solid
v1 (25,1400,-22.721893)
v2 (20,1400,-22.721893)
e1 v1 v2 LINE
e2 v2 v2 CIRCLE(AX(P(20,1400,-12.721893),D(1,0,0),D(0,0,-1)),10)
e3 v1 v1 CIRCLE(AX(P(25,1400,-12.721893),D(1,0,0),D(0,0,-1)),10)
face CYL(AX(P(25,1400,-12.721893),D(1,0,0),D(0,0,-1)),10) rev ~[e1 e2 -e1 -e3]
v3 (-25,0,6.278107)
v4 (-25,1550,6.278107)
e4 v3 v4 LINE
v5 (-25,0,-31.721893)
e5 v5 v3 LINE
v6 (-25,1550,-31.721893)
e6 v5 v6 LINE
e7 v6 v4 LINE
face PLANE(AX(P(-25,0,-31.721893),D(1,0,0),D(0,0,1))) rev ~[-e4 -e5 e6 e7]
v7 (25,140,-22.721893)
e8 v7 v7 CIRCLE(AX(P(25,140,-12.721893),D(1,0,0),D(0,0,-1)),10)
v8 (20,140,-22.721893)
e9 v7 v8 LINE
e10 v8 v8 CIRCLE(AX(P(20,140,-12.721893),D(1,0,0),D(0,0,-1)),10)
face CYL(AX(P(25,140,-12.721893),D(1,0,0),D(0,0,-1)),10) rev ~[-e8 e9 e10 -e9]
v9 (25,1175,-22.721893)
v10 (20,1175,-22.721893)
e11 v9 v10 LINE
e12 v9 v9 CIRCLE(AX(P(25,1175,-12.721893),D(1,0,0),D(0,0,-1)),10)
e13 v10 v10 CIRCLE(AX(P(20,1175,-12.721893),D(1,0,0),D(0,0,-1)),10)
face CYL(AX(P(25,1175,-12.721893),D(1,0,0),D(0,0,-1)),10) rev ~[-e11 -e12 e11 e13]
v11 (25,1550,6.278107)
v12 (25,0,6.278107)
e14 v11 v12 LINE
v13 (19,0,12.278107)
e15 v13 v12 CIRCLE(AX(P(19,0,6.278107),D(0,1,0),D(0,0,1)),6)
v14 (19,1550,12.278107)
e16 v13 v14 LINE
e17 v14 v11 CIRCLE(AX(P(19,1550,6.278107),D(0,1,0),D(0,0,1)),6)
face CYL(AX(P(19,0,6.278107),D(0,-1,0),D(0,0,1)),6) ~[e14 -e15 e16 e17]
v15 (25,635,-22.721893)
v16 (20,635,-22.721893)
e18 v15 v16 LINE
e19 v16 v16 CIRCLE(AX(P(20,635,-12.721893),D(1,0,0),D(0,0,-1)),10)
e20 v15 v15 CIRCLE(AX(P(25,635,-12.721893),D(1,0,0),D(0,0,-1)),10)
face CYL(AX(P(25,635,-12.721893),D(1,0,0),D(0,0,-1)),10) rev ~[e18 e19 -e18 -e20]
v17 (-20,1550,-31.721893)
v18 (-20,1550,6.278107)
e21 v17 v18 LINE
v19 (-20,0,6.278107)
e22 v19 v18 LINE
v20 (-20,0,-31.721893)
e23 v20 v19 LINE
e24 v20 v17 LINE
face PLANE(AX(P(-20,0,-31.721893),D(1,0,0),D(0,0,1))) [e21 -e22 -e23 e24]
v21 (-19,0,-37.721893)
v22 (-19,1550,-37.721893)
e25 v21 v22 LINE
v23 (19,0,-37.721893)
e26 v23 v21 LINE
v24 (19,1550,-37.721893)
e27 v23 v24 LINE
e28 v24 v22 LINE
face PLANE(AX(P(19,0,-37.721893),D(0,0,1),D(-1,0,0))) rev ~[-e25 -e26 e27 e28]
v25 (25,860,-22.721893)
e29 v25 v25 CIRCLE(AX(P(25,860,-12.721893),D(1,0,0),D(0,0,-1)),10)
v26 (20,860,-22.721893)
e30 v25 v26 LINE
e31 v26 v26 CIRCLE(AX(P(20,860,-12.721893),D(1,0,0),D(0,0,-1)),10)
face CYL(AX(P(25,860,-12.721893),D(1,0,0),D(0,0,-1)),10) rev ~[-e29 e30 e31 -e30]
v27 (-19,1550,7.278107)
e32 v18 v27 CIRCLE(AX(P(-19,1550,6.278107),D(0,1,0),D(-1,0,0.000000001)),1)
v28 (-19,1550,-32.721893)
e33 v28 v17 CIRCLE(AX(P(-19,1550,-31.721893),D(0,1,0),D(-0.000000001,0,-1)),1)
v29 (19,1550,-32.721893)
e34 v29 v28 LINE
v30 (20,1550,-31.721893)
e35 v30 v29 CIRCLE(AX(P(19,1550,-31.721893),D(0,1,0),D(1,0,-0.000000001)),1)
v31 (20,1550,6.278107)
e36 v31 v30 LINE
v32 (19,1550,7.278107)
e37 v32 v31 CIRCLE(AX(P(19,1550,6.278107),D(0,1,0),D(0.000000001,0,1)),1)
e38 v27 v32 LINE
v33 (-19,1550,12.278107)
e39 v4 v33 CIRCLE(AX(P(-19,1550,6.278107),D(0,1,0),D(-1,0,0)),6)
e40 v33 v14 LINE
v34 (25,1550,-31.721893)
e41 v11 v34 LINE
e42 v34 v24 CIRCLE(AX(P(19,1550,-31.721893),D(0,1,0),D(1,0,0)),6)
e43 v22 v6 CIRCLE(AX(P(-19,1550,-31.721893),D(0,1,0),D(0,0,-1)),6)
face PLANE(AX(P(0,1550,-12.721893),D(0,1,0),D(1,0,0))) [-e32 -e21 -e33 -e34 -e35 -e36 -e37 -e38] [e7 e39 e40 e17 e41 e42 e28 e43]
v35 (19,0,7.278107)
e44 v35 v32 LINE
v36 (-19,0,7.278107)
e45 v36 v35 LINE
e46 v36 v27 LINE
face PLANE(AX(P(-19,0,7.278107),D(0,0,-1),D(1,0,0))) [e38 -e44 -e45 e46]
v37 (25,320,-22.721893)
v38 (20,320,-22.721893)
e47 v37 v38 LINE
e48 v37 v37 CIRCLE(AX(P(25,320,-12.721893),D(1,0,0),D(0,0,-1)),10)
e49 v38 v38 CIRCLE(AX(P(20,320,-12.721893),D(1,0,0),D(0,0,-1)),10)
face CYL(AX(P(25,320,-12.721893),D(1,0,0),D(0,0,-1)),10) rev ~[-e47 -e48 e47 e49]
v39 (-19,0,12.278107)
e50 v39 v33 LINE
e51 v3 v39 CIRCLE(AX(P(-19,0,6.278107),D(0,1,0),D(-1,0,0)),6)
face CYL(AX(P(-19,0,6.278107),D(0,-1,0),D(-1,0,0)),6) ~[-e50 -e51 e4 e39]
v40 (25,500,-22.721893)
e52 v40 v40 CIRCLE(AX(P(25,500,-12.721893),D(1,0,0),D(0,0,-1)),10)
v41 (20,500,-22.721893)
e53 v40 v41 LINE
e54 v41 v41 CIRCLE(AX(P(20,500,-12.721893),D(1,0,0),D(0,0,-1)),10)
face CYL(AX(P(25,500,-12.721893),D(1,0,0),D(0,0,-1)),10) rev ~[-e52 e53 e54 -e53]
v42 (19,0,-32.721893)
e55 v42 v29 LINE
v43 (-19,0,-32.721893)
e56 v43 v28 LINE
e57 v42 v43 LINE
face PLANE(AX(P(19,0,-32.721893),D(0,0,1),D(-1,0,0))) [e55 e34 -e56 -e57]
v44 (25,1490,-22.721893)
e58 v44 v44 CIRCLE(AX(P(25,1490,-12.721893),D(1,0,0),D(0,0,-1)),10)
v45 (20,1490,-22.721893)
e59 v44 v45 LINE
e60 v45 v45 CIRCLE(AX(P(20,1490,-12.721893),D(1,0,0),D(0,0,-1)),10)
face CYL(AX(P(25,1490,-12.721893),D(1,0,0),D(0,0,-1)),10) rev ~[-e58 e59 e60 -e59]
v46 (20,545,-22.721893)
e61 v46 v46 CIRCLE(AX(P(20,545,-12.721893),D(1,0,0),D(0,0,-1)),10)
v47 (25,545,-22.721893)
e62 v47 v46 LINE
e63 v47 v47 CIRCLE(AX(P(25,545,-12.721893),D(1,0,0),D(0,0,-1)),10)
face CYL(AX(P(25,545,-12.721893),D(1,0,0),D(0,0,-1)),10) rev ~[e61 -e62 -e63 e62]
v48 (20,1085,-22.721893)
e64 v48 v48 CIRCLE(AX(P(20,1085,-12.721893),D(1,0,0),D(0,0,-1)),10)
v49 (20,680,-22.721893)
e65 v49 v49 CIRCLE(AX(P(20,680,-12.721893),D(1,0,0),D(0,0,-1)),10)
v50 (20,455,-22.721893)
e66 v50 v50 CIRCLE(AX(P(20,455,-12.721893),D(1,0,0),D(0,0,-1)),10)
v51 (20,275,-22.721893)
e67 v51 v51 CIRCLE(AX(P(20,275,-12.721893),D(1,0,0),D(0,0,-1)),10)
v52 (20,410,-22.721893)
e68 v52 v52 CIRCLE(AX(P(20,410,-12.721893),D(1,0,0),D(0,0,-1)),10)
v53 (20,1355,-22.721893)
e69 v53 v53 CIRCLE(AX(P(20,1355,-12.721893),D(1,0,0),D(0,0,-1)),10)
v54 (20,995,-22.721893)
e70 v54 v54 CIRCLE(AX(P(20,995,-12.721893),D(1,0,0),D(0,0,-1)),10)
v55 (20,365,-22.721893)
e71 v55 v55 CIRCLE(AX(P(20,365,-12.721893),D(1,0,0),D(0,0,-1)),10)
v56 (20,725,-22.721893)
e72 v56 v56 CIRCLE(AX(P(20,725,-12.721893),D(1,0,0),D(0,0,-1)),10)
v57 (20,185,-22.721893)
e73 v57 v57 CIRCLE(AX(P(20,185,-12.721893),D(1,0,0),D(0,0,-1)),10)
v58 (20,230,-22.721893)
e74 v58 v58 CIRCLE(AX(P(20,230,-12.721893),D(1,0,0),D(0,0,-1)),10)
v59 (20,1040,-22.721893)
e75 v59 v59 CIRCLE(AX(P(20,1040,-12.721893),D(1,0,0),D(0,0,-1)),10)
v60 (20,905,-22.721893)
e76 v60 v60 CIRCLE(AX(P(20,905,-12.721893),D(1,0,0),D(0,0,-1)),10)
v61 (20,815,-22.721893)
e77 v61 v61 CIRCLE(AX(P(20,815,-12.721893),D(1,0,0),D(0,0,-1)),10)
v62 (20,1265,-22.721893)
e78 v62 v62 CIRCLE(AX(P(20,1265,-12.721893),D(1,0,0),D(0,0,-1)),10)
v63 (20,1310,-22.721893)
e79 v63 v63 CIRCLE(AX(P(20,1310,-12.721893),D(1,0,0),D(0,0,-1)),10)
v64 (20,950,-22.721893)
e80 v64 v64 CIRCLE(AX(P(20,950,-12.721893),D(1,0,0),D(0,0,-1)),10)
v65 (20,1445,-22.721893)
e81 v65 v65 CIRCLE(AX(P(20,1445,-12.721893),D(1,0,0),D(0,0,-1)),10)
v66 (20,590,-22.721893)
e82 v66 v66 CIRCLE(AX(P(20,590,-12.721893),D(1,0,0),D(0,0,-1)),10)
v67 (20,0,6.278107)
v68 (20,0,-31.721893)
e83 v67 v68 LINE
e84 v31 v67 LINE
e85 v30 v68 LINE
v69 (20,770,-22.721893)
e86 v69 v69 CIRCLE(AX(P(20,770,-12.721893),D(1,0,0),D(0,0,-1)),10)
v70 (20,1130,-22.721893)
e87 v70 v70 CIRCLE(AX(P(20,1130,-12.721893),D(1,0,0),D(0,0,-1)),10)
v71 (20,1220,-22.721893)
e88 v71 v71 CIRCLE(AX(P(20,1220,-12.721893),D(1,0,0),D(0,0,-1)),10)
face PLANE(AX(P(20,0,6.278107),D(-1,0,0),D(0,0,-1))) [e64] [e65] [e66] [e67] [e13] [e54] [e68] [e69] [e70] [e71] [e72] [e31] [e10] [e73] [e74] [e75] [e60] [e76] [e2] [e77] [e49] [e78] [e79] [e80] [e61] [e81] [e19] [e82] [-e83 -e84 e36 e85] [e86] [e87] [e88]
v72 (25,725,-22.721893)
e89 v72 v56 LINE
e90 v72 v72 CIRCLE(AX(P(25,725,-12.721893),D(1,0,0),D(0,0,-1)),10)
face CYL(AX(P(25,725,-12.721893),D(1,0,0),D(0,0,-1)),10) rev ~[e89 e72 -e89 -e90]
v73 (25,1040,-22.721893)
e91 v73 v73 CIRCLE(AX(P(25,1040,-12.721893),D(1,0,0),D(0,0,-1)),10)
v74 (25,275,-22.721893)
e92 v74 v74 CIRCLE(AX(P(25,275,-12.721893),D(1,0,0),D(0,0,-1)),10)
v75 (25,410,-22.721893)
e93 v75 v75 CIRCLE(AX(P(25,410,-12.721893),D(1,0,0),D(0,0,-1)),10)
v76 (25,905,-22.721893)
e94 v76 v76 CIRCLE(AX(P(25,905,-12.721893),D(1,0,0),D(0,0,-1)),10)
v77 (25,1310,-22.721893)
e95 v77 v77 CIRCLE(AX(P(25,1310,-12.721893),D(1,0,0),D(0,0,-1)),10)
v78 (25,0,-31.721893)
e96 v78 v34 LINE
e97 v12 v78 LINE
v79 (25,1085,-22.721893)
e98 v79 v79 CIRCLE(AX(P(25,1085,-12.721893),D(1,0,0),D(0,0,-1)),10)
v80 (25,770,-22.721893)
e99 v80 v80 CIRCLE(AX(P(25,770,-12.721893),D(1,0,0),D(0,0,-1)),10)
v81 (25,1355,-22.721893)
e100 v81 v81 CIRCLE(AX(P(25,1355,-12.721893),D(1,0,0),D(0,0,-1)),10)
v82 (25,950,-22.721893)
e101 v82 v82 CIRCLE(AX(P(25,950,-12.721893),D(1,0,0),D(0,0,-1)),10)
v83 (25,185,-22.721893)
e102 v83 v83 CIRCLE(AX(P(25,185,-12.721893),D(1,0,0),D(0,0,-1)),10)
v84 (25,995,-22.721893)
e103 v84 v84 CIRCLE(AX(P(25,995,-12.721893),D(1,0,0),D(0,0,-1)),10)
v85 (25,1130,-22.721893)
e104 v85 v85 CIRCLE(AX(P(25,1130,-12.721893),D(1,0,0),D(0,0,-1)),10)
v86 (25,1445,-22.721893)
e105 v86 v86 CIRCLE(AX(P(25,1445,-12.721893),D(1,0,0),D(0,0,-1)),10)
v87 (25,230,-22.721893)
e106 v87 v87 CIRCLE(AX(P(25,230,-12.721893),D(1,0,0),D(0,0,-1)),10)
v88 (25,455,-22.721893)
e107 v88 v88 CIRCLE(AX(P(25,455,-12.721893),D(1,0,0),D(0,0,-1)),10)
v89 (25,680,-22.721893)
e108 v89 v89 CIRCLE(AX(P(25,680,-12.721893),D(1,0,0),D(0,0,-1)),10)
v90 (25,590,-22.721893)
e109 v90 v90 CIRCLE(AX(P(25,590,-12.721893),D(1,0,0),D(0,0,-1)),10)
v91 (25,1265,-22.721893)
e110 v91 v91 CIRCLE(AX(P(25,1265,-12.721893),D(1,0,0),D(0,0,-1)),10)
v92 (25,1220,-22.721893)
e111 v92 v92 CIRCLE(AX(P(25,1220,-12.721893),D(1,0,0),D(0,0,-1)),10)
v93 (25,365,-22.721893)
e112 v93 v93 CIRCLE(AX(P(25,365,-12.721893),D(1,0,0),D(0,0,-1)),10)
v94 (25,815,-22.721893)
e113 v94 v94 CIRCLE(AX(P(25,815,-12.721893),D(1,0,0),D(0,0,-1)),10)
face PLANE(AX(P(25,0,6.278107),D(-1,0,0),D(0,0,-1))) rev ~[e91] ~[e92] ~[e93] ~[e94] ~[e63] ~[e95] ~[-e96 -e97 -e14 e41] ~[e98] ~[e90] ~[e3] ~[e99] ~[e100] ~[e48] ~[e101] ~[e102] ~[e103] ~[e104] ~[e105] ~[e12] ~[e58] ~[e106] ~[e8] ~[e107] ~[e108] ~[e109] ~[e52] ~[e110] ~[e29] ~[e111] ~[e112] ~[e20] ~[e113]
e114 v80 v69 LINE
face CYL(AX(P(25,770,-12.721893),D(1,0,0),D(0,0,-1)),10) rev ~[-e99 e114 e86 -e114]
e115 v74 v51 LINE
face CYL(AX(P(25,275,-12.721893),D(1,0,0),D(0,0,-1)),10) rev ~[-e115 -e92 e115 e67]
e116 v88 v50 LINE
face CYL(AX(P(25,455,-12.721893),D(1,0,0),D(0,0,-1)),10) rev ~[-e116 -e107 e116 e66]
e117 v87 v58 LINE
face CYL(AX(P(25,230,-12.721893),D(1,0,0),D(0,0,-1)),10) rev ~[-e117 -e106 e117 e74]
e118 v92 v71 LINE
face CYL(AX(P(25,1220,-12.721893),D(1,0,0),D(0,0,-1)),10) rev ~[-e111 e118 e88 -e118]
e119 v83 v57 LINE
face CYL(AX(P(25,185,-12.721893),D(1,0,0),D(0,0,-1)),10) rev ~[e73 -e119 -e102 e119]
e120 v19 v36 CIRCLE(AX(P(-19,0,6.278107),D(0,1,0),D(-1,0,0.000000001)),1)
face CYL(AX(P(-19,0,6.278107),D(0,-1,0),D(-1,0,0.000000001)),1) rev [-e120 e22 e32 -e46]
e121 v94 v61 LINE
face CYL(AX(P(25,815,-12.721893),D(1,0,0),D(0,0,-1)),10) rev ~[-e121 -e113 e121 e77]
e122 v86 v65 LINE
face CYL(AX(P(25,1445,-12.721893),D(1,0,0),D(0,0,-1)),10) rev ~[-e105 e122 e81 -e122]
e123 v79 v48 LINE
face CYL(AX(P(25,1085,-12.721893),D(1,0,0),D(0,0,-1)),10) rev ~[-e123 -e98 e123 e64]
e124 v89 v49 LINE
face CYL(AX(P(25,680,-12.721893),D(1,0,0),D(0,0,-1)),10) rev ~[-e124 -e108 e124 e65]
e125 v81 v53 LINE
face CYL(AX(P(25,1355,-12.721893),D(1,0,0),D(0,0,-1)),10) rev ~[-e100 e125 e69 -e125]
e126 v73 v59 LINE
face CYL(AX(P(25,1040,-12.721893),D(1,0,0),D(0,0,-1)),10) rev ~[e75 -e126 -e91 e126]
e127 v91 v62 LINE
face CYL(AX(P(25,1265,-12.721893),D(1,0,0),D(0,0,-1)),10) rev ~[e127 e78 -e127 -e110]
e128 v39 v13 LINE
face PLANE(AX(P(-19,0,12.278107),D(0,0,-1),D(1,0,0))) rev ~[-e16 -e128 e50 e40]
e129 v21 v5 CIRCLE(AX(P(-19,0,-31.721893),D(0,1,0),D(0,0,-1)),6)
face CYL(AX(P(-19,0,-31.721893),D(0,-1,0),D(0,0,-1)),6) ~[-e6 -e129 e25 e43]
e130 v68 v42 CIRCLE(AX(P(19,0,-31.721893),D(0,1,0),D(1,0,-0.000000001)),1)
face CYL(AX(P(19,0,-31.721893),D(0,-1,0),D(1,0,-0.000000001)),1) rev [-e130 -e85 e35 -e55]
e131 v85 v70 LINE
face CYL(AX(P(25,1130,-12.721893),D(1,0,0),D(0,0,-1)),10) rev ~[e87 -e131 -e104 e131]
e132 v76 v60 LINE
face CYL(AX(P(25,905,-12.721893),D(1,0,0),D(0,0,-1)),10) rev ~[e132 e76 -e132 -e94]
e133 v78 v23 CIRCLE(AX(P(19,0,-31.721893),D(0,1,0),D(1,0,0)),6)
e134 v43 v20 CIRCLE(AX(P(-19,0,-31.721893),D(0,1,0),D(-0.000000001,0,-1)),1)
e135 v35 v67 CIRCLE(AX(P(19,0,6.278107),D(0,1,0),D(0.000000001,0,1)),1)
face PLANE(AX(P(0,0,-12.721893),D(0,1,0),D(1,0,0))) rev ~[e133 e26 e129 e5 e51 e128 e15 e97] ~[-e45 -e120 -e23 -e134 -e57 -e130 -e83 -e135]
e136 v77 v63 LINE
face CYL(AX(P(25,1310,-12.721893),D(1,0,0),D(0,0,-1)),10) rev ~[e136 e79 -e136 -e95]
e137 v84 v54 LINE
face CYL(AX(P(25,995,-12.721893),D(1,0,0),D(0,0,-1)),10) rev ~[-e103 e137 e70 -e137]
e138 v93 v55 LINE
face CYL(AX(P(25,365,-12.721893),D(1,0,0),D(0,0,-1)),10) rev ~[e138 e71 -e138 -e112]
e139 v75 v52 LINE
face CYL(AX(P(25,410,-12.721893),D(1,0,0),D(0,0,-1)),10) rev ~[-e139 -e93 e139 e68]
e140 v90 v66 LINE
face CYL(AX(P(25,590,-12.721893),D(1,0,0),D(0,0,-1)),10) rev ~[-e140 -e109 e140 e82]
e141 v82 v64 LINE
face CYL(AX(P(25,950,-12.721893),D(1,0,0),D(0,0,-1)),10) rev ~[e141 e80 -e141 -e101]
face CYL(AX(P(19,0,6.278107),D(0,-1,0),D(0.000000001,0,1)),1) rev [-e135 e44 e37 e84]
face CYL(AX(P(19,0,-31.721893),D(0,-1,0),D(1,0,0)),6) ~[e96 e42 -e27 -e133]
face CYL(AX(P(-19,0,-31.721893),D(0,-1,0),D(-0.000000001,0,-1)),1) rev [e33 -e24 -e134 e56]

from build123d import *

# Parameters (mm, degrees)
EXTRUDE_1_DEPTH     = 1550
SKETCH_2_R          = 12
CUT_EXTRUDE_1_DEPTH = 10
SKETCH_3_R          = 16.065065839
SKETCH_3_R_2        = 15.441664685
EXTRUDE_2_DEPTH     = 5
SKETCH_4_W          = 38
SKETCH_4_H          = 630.491026123
EXTRUDE_3_DEPTH     = 5
SKETCH_5_R          = 10
CUT_EXTRUDE_2_DEPTH = 10


with BuildPart() as part:
    # 草图1 → 凸台-拉伸1 (new body)
    with BuildSketch(Plane(origin=(0, 0, 0), x_dir=(1, 0, 0), z_dir=(0, 1, 0))):
        with BuildLine():
            Line((-19, -12.278106509), (19, -12.278106509))
            ThreePointArc((19, -12.278106509), (23.242640687, -10.520747196), (25, -6.278106509))
            Line((25, -6.278106509), (25, 31.721893491))
            ThreePointArc((25, 31.721893491), (23.242640687, 35.964534178), (19, 37.721893491))
            Line((19, 37.721893491), (-19, 37.721893491))
            ThreePointArc((-19, 37.721893491), (-23.242640687, 35.964534178), (-25, 31.721893491))
            Line((-25, 31.721893491), (-25, -6.278106509))
            ThreePointArc((-25, -6.278106509), (-23.242640687, -10.520747196), (-19, -12.278106509))
        make_face()
        with BuildLine():
            Line((-19, -7.278106509), (19, -7.278106509))
            ThreePointArc((19, -7.278106509), (19.707106781, -6.98521329), (20, -6.278106509))
            Line((20, -6.278106509), (20, 31.721893491))
            ThreePointArc((20, 31.721893491), (19.707106781, 32.429000272), (19, 32.721893491))
            Line((19, 32.721893491), (-19, 32.721893491))
            ThreePointArc((-19, 32.721893491), (-19.707106781, 32.429000272), (-20, 31.721893491))
            Line((-20, 31.721893491), (-20, -6.278106509))
            ThreePointArc((-20, -6.278106509), (-19.707106781, -6.98521329), (-19, -7.278106509))
        make_face(mode=Mode.SUBTRACT)
    extrude(amount=EXTRUDE_1_DEPTH)

    # 草图2 → 切除-拉伸1 (cut)
    with BuildSketch(Plane(origin=(25, 0, 0), x_dir=(0, 0, -1), z_dir=(1, 0, 0))):
        with Locations((12.721893491, 1527.5)):
            Circle(SKETCH_2_R)
        with Locations((12.721893491, 1482.5)):
            Circle(SKETCH_2_R)
        with Locations((12.721893491, 1437.5)):
            Circle(SKETCH_2_R)
        with Locations((12.721893491, 1392.5)):
            Circle(SKETCH_2_R)
        with Locations((12.721893491, 1347.5)):
            Circle(SKETCH_2_R)
        with Locations((12.721893491, 1302.5)):
            Circle(SKETCH_2_R)
        with Locations((12.721893491, 1257.5)):
            Circle(SKETCH_2_R)
        with Locations((12.721893491, 1212.5)):
            Circle(SKETCH_2_R)
        with Locations((12.721893491, 1167.5)):
            Circle(SKETCH_2_R)
        with Locations((12.721893491, 1122.5)):
            Circle(SKETCH_2_R)
        with Locations((12.721893491, 1077.5)):
            Circle(SKETCH_2_R)
        with Locations((12.721893491, 1032.5)):
            Circle(SKETCH_2_R)
        with Locations((12.721893491, 987.5)):
            Circle(SKETCH_2_R)
        with Locations((12.721893491, 942.5)):
            Circle(SKETCH_2_R)
        with Locations((12.721893491, 897.5)):
            Circle(SKETCH_2_R)
    extrude(amount=-CUT_EXTRUDE_1_DEPTH, mode=Mode.SUBTRACT)

    # 草图3 → 凸台-拉伸2 (add)
    with BuildSketch(Plane(origin=(25, 0, 0), x_dir=(0, 0, -1), z_dir=(1, 0, 0))):
        with Locations((12.721893491, 897.5)):
            Circle(SKETCH_3_R)
        with Locations((12.721893491, 1527.5)):
            Circle(SKETCH_3_R_2)
    extrude(amount=-EXTRUDE_2_DEPTH)

    # 草图4 → 凸台-拉伸3 (add)
    with BuildSketch(Plane(origin=(25, 0, 0), x_dir=(0, 0, -1), z_dir=(1, 0, 0))):
        with Locations((12.721893491, 1196.647134408)):
            Rectangle(SKETCH_4_W, SKETCH_4_H)
    extrude(amount=-EXTRUDE_3_DEPTH)

    # 草图5 → 切除-拉伸2 (cut)
    with BuildSketch(Plane(origin=(25, 0, 0), x_dir=(0, 0, -1), z_dir=(1, 0, 0))):
        with Locations((12.721893491, 1490)):
            Circle(SKETCH_5_R)
        with Locations((12.721893491, 1445)):
            Circle(SKETCH_5_R)
        with Locations((12.721893491, 1400)):
            Circle(SKETCH_5_R)
        with Locations((12.721893491, 1355)):
            Circle(SKETCH_5_R)
        with Locations((12.721893491, 1310)):
            Circle(SKETCH_5_R)
        with Locations((12.721893491, 1265)):
            Circle(SKETCH_5_R)
        with Locations((12.721893491, 1220)):
            Circle(SKETCH_5_R)
        with Locations((12.721893491, 1175)):
            Circle(SKETCH_5_R)
        with Locations((12.721893491, 1130)):
            Circle(SKETCH_5_R)
        with Locations((12.721893491, 1085)):
            Circle(SKETCH_5_R)
        with Locations((12.721893491, 1040)):
            Circle(SKETCH_5_R)
        with Locations((12.721893491, 995)):
            Circle(SKETCH_5_R)
        with Locations((12.721893491, 950)):
            Circle(SKETCH_5_R)
        with Locations((12.721893491, 905)):
            Circle(SKETCH_5_R)
        with Locations((12.721893491, 860)):
            Circle(SKETCH_5_R)
        with Locations((12.721893491, 815)):
            Circle(SKETCH_5_R)
        with Locations((12.721893491, 770)):
            Circle(SKETCH_5_R)
        with Locations((12.721893491, 725)):
            Circle(SKETCH_5_R)
        with Locations((12.721893491, 680)):
            Circle(SKETCH_5_R)
        with Locations((12.721893491, 635)):
            Circle(SKETCH_5_R)
        with Locations((12.721893491, 590)):
            Circle(SKETCH_5_R)
        with Locations((12.721893491, 545)):
            Circle(SKETCH_5_R)
        with Locations((12.721893491, 500)):
            Circle(SKETCH_5_R)
        with Locations((12.721893491, 455)):
            Circle(SKETCH_5_R)
        with Locations((12.721893491, 410)):
            Circle(SKETCH_5_R)
        with Locations((12.721893491, 365)):
            Circle(SKETCH_5_R)
        with Locations((12.721893491, 320)):
            Circle(SKETCH_5_R)
        with Locations((12.721893491, 275)):
            Circle(SKETCH_5_R)
        with Locations((12.721893491, 230)):
            Circle(SKETCH_5_R)
        with Locations((12.721893491, 185)):
            Circle(SKETCH_5_R)
        with Locations((12.721893491, 140)):
            Circle(SKETCH_5_R)
    extrude(amount=-CUT_EXTRUDE_2_DEPTH, mode=Mode.SUBTRACT)


solid = part.part
